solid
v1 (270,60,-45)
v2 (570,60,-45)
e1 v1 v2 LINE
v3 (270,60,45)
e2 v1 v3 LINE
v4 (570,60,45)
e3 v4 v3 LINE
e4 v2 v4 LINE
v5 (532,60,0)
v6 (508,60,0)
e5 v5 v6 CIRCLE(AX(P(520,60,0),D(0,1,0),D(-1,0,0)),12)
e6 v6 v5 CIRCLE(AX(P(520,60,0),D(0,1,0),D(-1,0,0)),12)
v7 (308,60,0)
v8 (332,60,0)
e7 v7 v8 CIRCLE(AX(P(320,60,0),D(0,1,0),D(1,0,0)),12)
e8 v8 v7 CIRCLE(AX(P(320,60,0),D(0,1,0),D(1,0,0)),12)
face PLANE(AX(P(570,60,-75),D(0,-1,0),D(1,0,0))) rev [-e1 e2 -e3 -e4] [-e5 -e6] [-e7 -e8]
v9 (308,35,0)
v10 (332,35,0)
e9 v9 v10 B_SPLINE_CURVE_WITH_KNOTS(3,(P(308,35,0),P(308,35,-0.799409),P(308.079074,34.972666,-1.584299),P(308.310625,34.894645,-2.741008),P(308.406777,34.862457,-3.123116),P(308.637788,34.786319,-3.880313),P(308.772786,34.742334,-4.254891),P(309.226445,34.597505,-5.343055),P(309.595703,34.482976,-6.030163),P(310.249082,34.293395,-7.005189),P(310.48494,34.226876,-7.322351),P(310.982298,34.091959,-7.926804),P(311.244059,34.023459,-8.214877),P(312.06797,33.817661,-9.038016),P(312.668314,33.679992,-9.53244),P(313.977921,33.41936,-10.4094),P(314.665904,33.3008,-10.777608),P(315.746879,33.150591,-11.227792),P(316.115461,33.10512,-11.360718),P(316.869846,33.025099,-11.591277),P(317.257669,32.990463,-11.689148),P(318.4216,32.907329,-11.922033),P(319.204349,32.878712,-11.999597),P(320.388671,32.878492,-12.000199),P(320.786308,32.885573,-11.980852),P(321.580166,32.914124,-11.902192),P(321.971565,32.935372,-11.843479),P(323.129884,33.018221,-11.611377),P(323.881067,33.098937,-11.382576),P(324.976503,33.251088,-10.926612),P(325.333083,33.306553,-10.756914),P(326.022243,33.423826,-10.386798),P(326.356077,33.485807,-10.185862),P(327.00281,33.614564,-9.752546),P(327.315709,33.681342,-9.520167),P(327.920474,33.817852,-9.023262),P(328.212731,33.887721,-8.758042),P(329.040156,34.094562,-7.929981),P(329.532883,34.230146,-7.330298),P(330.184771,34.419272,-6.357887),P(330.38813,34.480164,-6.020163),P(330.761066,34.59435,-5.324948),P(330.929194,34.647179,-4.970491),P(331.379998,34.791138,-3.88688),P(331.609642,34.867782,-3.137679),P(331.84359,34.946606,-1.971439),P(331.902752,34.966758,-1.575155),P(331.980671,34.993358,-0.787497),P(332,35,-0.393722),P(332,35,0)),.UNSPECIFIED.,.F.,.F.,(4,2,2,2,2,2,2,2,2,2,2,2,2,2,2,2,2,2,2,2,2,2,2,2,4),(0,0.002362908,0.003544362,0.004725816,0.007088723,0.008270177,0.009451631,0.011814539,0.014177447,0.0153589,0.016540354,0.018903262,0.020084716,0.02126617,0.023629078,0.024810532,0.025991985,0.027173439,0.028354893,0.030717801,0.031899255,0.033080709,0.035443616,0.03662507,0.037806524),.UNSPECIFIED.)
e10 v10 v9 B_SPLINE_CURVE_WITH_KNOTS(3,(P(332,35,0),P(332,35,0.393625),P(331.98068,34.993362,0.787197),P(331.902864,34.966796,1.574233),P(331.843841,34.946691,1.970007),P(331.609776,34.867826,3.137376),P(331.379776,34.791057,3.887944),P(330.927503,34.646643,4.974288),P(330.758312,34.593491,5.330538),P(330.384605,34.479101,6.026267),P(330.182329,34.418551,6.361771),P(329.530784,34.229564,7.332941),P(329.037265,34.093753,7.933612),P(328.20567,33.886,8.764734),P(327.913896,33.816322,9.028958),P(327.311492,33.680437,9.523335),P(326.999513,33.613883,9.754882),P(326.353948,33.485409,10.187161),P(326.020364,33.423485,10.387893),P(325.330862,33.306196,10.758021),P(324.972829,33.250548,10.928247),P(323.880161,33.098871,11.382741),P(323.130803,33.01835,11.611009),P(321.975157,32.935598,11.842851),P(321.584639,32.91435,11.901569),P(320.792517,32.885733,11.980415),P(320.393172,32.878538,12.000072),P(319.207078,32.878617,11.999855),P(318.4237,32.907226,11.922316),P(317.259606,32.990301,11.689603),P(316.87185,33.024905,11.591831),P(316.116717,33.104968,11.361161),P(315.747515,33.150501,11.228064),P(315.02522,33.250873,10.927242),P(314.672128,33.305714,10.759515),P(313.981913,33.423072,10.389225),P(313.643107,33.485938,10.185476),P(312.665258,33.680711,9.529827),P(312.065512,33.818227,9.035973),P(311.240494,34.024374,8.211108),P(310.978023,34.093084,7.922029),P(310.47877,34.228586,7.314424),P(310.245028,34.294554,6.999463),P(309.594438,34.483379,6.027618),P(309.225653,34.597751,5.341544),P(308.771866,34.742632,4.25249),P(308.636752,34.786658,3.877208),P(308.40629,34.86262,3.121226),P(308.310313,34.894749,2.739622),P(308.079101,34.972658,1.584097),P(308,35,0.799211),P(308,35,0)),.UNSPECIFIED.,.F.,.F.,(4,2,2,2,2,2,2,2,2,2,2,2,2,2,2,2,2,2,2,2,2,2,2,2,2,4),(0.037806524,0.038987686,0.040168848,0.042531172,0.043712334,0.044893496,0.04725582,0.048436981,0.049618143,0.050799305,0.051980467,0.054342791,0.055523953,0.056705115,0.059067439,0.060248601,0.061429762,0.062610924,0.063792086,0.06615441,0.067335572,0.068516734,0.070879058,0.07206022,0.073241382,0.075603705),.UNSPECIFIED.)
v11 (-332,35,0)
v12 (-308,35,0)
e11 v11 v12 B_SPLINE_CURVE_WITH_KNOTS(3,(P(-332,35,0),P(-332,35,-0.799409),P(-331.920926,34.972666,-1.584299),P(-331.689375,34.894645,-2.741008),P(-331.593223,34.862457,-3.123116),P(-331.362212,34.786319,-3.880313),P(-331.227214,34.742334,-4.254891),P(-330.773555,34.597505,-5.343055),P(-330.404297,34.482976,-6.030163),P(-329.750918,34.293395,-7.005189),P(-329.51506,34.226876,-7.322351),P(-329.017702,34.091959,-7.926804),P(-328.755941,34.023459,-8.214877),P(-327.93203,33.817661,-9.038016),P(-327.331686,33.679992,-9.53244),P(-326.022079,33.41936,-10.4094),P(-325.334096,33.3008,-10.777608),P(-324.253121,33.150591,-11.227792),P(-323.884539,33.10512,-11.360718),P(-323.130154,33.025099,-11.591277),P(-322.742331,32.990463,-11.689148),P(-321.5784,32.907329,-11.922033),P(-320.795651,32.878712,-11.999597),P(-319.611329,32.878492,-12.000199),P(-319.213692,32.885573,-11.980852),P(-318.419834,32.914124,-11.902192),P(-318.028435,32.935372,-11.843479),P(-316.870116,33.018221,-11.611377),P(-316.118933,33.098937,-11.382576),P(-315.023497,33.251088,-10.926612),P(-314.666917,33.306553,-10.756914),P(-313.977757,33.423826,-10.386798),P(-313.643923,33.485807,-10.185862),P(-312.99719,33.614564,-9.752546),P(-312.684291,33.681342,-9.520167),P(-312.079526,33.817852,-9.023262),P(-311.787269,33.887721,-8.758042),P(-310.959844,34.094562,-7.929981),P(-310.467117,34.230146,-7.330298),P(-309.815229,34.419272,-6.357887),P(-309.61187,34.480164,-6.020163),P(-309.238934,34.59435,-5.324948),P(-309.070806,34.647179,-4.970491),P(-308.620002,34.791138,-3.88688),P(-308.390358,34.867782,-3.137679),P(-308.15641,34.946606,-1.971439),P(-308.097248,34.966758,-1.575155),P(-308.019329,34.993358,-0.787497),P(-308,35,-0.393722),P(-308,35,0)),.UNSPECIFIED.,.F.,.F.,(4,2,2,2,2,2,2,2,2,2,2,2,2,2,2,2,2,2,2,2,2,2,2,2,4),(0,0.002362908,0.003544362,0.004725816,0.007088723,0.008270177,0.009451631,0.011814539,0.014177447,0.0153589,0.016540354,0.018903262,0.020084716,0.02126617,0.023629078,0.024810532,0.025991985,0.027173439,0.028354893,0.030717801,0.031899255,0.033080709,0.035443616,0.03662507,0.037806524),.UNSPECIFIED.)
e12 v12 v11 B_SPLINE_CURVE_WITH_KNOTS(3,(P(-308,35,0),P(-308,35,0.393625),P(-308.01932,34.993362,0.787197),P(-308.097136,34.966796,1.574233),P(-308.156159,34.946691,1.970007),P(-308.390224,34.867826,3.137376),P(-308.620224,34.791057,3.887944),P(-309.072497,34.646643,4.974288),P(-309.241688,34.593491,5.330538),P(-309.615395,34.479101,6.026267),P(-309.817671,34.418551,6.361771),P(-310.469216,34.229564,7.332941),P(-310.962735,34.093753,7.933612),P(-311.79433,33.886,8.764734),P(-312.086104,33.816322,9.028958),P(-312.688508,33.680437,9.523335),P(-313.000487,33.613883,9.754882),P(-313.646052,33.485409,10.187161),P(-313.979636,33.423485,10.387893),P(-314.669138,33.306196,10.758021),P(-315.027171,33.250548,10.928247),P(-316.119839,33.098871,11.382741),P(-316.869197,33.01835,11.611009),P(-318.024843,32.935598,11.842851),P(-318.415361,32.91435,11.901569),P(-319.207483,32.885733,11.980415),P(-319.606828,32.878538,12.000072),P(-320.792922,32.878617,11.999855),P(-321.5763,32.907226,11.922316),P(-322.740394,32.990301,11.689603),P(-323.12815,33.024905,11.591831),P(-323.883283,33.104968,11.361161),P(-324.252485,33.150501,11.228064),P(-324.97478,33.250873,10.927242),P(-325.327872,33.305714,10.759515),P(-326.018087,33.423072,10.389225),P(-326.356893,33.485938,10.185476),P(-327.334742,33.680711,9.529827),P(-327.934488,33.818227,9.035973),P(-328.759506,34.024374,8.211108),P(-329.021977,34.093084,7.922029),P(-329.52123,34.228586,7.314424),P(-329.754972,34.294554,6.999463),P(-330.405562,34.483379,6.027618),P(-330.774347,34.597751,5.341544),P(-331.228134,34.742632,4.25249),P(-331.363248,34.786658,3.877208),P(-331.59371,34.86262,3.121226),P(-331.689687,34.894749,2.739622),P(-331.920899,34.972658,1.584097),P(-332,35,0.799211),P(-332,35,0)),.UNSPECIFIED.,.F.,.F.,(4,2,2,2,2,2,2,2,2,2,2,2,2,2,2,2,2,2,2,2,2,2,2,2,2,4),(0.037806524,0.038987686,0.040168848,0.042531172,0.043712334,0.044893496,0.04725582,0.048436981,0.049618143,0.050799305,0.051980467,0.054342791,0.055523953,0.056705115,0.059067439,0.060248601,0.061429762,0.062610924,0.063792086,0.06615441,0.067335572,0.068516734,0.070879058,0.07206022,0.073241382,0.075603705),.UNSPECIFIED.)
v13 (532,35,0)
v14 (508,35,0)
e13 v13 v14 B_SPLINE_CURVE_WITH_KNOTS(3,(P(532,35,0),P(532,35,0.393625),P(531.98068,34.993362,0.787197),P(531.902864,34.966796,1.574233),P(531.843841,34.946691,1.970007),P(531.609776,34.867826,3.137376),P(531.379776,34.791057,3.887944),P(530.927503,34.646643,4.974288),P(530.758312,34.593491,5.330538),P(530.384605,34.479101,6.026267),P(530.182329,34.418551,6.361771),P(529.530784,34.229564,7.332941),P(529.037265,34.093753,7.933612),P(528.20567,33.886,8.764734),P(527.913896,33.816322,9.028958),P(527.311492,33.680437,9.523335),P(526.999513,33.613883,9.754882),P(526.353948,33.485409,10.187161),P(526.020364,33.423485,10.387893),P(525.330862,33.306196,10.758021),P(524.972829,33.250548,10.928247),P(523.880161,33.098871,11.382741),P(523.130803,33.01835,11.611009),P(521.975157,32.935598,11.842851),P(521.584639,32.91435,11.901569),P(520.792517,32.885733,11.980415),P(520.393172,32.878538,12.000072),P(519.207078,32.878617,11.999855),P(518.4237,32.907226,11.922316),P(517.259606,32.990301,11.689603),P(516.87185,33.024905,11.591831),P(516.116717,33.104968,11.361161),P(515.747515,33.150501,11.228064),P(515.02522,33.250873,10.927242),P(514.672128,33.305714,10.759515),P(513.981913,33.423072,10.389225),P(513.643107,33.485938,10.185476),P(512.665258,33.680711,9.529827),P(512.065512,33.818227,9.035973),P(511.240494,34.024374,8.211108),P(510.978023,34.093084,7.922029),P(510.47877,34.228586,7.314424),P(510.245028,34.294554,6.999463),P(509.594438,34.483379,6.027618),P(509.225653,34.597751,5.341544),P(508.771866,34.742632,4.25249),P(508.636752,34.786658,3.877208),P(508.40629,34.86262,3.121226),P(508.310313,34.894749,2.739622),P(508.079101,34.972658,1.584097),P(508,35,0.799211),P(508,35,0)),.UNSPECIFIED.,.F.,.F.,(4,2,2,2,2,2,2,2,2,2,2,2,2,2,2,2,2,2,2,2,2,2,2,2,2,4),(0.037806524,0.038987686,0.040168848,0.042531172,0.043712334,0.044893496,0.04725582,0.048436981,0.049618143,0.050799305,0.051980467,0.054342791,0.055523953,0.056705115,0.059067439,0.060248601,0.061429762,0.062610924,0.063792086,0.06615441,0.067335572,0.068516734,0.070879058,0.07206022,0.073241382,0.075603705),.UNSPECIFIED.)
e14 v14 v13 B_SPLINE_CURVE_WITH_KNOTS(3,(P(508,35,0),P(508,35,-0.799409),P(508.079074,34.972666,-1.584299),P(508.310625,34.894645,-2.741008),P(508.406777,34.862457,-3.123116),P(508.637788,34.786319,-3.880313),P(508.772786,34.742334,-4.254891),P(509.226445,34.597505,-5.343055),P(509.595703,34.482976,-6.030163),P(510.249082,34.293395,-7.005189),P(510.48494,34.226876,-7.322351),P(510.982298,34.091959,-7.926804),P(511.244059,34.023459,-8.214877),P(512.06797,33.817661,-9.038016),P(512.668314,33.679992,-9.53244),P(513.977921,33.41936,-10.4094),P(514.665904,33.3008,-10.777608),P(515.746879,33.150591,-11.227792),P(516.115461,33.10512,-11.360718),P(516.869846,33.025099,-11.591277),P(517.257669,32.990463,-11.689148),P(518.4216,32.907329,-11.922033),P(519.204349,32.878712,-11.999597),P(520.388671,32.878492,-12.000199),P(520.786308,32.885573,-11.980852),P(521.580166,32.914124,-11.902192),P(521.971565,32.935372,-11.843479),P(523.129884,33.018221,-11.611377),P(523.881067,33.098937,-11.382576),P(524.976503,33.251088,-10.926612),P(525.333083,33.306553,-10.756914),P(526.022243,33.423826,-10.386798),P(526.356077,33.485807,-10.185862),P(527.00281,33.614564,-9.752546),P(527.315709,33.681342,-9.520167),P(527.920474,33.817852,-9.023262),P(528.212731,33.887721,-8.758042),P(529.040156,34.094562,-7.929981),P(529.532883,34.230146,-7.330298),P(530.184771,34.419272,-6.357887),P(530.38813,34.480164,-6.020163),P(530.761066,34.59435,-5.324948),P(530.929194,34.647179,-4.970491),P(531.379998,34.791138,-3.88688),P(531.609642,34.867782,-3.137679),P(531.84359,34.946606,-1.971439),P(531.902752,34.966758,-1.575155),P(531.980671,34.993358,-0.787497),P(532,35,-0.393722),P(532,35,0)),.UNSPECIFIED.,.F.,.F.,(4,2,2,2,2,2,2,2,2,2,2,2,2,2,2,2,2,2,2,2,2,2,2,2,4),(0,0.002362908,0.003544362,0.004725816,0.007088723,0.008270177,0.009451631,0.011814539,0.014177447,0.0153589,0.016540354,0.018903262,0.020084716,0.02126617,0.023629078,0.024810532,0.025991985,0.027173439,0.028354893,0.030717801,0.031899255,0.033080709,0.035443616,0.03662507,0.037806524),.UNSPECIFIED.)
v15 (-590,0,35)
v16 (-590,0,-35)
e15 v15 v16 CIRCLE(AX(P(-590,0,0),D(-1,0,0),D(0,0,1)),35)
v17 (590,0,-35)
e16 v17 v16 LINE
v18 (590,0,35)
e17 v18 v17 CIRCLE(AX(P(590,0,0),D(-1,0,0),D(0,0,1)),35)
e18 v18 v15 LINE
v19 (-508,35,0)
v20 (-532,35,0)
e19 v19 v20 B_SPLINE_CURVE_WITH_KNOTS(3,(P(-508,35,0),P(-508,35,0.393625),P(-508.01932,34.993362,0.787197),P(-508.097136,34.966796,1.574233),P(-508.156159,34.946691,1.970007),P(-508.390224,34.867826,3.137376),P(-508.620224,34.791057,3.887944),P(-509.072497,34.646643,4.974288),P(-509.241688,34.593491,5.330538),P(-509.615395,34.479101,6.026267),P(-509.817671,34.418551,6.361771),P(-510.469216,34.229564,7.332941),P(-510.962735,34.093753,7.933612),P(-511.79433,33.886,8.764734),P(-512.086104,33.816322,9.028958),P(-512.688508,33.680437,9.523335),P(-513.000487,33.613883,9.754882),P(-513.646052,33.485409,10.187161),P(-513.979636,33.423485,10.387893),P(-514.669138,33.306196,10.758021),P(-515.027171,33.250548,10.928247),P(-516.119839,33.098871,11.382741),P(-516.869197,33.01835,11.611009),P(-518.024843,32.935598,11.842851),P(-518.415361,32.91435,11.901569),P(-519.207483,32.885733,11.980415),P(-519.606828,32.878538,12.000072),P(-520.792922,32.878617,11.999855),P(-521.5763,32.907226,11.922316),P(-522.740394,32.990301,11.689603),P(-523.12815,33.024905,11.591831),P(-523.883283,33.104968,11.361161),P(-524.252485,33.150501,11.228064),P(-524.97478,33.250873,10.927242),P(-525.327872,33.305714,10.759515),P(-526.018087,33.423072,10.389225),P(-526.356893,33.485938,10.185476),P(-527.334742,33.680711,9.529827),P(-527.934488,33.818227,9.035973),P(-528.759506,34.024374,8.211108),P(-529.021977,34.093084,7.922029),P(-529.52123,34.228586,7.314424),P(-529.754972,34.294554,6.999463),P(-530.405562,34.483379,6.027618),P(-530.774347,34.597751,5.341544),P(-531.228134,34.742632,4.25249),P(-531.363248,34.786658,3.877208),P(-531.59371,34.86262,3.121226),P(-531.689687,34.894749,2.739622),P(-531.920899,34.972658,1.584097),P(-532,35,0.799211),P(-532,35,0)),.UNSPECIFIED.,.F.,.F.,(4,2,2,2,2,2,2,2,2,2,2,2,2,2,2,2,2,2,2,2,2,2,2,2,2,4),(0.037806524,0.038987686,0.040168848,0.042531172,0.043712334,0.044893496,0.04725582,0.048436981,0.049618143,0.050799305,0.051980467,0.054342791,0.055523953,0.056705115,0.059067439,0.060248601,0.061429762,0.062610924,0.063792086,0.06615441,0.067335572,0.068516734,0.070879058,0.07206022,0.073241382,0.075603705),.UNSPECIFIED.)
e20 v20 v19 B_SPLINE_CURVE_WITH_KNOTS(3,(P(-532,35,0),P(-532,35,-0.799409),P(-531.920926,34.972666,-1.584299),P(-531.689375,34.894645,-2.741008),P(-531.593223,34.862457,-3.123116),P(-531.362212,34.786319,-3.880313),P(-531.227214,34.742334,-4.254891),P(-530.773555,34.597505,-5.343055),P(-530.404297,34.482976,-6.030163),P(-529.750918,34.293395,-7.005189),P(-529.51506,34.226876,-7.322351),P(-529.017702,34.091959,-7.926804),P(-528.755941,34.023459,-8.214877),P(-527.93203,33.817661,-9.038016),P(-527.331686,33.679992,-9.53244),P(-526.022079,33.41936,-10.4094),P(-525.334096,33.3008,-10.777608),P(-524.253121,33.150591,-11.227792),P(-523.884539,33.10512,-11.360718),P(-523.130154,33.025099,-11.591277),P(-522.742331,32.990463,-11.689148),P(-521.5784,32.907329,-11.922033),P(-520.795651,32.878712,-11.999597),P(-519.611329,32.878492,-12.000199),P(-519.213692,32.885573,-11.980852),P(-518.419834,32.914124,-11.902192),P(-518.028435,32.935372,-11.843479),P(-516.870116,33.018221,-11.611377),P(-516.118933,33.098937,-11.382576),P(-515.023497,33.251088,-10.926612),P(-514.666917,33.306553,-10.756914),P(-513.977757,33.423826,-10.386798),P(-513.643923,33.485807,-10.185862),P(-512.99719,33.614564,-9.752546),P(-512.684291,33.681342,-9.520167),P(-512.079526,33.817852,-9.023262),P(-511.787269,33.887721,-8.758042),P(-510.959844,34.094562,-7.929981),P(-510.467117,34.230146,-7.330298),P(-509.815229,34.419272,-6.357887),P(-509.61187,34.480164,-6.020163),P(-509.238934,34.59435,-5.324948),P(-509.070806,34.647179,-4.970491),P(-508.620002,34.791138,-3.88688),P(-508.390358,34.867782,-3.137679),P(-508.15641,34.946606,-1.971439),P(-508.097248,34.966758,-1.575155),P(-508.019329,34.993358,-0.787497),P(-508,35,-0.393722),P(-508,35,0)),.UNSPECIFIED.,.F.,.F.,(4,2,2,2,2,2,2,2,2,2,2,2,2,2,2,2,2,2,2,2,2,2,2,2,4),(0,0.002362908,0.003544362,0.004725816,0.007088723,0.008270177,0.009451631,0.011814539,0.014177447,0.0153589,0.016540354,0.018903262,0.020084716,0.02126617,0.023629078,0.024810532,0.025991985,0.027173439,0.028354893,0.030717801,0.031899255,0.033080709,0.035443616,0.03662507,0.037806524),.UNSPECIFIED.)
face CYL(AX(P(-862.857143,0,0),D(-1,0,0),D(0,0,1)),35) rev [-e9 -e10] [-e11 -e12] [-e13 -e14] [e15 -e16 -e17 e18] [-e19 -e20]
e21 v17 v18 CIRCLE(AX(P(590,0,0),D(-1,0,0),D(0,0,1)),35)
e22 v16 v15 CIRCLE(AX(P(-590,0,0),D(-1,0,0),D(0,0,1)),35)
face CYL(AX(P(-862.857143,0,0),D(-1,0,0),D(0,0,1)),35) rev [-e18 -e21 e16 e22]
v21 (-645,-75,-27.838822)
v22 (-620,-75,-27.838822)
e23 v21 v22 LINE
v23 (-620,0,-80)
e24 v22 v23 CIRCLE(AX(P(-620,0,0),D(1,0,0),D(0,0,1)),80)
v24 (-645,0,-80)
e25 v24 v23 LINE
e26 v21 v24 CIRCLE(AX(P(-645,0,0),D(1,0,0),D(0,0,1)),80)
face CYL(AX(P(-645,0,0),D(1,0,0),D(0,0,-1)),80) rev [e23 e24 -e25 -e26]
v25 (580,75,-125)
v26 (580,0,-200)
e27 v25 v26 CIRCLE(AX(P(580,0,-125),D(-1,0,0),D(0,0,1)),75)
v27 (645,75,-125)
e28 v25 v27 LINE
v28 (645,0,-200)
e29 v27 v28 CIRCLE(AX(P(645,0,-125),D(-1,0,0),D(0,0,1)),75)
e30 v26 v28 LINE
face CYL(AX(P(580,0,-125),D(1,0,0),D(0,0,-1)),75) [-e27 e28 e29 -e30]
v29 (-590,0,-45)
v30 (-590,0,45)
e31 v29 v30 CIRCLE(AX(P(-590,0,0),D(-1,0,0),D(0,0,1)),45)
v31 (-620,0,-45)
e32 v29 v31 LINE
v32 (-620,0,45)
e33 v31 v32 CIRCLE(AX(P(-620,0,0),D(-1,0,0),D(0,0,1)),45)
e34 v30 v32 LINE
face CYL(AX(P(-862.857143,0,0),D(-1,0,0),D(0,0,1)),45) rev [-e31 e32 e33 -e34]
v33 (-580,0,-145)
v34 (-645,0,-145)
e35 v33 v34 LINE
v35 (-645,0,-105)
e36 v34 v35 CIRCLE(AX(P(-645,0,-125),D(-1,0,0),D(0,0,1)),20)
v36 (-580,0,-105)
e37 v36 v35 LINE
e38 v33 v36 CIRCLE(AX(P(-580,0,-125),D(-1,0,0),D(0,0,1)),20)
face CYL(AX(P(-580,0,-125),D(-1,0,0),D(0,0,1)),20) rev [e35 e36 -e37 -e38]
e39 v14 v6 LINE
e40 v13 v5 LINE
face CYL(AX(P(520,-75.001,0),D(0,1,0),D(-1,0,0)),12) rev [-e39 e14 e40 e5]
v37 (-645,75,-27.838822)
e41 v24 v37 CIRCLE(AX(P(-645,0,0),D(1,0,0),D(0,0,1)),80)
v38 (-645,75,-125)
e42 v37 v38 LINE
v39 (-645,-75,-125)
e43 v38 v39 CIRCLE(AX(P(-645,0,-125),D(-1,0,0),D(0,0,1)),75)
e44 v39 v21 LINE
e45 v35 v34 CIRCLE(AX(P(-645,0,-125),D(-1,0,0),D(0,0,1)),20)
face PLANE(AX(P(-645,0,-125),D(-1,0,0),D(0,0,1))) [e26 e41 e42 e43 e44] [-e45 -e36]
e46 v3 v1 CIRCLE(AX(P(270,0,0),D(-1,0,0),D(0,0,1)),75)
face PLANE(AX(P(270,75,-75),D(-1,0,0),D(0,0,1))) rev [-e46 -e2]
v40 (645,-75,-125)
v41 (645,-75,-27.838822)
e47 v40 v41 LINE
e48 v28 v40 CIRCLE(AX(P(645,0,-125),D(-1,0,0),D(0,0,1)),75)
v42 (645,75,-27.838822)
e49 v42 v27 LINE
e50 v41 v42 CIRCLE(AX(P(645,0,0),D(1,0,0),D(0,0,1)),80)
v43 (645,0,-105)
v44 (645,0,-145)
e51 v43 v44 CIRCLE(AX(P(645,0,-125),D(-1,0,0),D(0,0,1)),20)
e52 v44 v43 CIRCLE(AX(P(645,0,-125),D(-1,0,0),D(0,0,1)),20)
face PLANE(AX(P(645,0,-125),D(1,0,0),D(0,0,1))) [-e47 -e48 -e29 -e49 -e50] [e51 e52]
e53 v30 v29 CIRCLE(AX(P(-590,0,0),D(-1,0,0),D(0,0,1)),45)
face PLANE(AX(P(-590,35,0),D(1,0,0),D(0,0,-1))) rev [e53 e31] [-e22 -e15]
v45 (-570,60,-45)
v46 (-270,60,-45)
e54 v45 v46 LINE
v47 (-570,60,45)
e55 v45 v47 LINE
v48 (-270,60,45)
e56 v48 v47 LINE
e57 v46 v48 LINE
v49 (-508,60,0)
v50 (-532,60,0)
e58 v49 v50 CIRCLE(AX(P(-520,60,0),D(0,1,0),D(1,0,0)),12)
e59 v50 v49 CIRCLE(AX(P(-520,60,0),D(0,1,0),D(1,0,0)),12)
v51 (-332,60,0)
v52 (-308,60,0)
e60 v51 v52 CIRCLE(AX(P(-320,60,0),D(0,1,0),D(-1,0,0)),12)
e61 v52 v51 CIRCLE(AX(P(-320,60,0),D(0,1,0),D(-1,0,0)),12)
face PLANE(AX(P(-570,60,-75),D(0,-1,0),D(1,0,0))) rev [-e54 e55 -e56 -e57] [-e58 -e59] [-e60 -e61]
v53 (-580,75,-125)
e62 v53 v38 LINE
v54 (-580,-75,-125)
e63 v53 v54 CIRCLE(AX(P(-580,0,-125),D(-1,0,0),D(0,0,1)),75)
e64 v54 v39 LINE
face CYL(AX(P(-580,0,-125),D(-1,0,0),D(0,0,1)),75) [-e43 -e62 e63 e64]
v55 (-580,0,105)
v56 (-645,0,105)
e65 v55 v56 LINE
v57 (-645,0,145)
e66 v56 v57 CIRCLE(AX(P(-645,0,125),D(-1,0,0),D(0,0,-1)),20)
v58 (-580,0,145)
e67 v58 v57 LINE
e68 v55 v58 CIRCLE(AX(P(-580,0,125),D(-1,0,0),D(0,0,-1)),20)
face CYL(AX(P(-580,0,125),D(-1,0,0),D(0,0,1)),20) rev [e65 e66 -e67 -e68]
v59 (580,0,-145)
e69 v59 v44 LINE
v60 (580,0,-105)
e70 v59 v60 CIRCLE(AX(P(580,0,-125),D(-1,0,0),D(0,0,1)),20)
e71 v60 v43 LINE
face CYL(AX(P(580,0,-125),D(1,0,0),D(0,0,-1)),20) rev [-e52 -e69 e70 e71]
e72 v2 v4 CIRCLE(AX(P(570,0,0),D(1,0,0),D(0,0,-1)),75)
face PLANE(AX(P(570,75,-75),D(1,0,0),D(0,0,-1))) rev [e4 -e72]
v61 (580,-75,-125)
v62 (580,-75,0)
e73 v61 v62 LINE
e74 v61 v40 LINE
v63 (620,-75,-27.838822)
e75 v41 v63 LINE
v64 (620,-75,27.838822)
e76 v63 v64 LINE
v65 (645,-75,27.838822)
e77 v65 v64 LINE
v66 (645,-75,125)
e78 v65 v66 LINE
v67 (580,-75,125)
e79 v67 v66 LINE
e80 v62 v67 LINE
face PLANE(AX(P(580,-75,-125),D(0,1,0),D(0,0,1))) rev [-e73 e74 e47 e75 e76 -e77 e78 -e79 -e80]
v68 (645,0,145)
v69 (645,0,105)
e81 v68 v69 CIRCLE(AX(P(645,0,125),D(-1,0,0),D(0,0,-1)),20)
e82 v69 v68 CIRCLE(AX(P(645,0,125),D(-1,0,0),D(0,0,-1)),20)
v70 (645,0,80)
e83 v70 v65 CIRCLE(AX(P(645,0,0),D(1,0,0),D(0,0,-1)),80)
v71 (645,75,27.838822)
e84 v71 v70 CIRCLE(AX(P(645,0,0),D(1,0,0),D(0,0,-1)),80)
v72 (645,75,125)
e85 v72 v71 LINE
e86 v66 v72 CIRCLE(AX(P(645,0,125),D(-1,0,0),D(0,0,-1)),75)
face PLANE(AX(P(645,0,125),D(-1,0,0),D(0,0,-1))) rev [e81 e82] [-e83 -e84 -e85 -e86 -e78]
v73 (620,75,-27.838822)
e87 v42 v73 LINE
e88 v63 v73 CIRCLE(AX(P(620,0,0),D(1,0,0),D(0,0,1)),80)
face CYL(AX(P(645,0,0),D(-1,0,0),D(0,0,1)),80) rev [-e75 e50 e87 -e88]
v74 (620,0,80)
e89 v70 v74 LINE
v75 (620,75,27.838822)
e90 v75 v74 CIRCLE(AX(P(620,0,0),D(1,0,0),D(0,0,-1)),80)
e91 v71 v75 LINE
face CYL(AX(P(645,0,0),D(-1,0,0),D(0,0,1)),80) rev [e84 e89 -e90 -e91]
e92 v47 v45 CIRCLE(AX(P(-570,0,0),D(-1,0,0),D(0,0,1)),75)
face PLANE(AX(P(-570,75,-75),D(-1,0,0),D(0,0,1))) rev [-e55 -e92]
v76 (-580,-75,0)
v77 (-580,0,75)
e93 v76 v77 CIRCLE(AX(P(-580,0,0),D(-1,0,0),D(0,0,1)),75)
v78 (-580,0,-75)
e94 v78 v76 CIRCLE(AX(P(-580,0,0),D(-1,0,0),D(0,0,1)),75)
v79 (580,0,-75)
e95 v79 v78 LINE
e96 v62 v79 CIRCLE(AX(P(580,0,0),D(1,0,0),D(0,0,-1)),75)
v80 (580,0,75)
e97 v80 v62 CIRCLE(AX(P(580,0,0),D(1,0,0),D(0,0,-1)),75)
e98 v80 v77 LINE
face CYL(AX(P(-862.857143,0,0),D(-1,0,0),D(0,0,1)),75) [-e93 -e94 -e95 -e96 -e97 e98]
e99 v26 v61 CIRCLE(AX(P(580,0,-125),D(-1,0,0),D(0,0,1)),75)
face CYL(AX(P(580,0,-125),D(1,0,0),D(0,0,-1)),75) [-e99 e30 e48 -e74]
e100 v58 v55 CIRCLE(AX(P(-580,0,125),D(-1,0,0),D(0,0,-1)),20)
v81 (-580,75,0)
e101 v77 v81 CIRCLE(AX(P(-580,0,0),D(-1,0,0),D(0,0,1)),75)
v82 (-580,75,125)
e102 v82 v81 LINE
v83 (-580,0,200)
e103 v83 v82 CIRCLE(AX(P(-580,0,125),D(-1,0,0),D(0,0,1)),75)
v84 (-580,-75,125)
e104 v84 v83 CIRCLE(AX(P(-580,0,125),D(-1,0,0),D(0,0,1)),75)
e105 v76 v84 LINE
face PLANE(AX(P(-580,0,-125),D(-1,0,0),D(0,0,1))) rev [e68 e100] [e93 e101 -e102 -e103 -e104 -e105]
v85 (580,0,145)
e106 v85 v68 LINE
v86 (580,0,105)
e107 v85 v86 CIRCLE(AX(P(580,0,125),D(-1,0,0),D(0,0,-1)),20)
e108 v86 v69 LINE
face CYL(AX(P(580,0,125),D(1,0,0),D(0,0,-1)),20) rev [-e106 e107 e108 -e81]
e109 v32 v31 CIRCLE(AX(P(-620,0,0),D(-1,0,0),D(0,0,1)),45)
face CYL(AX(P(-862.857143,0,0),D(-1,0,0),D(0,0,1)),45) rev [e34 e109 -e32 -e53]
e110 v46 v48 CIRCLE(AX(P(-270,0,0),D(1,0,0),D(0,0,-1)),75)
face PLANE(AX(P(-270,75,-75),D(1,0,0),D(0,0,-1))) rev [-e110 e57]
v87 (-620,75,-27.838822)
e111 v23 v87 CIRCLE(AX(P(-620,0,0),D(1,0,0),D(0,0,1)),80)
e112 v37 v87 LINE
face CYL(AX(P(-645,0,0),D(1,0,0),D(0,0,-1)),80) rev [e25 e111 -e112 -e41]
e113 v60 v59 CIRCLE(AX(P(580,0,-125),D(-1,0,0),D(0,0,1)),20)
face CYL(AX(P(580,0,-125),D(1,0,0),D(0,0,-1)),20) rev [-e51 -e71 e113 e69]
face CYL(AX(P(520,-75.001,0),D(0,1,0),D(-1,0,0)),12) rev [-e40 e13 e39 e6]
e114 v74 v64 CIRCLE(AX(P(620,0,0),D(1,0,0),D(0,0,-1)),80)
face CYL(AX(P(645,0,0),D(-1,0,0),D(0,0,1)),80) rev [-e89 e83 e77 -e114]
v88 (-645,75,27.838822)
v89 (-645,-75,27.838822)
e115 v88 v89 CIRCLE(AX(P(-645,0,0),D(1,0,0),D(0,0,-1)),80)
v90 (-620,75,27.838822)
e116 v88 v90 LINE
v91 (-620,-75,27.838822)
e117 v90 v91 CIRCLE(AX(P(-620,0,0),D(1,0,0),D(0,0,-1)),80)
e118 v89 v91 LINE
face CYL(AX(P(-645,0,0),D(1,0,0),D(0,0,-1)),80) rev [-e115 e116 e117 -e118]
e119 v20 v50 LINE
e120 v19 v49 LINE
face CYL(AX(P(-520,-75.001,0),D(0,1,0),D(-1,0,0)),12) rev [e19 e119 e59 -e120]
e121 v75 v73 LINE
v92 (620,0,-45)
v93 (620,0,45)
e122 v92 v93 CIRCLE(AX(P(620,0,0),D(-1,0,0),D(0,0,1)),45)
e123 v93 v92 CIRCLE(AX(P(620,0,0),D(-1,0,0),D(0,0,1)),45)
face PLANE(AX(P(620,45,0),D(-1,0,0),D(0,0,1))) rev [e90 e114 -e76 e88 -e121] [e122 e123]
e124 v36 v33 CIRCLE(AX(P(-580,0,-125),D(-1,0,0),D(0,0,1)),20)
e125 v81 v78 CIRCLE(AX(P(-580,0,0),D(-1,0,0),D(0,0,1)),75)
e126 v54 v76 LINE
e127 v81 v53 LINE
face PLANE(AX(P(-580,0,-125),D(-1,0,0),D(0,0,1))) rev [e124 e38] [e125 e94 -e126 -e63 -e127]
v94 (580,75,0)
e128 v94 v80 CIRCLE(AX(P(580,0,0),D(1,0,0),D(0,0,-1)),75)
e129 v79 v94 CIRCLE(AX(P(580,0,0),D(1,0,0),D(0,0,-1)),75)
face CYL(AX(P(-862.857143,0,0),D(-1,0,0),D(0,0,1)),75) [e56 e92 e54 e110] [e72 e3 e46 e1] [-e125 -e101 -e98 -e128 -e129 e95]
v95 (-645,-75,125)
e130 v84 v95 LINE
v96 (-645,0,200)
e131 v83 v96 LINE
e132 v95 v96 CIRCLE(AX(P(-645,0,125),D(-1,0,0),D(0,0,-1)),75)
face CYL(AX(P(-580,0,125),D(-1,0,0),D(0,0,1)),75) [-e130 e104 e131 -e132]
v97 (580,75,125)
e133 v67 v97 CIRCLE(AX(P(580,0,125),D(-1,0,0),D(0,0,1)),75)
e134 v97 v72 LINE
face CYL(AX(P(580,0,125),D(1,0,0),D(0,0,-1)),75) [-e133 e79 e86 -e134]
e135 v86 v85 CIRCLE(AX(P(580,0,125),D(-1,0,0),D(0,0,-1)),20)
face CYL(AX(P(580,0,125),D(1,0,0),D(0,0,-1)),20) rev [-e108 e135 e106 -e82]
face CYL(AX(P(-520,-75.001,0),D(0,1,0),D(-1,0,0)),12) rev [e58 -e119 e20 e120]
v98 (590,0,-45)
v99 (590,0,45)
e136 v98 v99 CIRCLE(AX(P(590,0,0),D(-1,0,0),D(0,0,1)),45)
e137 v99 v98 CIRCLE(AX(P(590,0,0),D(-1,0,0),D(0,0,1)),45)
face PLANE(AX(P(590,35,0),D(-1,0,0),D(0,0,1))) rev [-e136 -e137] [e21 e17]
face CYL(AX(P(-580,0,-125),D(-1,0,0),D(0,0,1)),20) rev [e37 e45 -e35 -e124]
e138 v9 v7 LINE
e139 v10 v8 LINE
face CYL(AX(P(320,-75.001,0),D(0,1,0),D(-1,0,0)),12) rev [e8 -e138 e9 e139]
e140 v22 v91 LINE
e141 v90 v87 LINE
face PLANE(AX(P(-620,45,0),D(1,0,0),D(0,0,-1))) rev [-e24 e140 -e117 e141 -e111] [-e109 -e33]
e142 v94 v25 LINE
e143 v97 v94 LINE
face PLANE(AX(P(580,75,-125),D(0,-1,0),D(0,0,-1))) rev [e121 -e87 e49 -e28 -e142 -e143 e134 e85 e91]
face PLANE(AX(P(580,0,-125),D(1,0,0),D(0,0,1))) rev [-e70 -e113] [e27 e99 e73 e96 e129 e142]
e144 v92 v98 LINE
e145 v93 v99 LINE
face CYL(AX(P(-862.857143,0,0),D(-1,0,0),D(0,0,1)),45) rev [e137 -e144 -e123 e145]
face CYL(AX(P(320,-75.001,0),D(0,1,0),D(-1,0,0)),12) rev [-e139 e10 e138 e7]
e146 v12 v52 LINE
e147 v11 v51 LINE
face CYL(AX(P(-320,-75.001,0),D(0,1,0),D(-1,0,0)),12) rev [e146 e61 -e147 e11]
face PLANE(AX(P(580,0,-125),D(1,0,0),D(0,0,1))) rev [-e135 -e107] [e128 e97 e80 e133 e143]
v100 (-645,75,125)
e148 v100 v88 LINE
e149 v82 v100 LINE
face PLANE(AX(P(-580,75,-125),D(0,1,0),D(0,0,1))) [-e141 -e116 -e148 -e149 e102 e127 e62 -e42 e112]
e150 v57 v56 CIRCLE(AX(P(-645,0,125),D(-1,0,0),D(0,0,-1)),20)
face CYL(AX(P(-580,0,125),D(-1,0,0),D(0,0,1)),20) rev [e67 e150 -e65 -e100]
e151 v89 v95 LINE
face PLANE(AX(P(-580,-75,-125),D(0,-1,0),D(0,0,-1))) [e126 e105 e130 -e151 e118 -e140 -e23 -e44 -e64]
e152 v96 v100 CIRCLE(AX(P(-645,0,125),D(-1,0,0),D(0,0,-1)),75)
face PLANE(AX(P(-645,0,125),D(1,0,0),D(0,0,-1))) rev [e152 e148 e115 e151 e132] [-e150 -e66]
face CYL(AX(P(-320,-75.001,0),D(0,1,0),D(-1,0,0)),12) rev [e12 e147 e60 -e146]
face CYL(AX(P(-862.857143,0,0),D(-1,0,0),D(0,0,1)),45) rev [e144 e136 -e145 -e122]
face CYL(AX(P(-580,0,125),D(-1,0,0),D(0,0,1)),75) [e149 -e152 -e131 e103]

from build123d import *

# Parameters (mm, degrees)
CUT_EXTRUDE_1_DEPTH      = 630.007154172
CUT_EXTRUDE_1_DEPTH_BACK = 630.007154172
SKETCH_2_W               = 300
SKETCH_2_H               = 15
CUT_EXTRUDE_2_REACH      = 640.944
CUT_EXTRUDE_2_END_RADIUS = 35
SKETCH_3_R               = 12
SKETCH_4_R               = 20
SKETCH_4_R_2             = 45
BOSS_EXTRUDE_1_DEPTH     = 40
BOSS_EXTRUDE_START       = 25
SKETCH_5_R               = 20
BOSS_EXTRUDE_2_DEPTH     = 25


with BuildPart() as part:
    # Sketch 1 → Revolve 1 (revolve)
    with BuildSketch(Plane.XY, mode=Mode.PRIVATE) as revolve_1_sk:
        Polygon((590, 35), (-590, 35), (-590, 45), (-620, 45), (-620, 75), (620, 75), (620, 45), (590, 45), align=None)
    revolve(revolve_1_sk.sketch.rotate(Axis((-862.857142857, 0, 0), (1, 0, 0)), 90), axis=Axis((-862.857142857, 0, 0), (1, 0, 0)))

    # Sketch 2 → Cut-Extrude 1 (cut, two sides: drawn at the far end of the back side and taken through both)
    with BuildSketch(Plane.XY.offset(-CUT_EXTRUDE_1_DEPTH_BACK)):
        with Locations((-420, 67.5)):
            Rectangle(SKETCH_2_W, SKETCH_2_H)
        with Locations((420, 67.5)):
            Rectangle(SKETCH_2_W, SKETCH_2_H)
    extrude(amount=CUT_EXTRUDE_1_DEPTH + CUT_EXTRUDE_1_DEPTH_BACK, mode=Mode.SUBTRACT)

    # Cut-Extrude 2: up to this cylinder (the profile starts outside it)
    cut_extrude_2_end = Plane(origin=(0, 0, 0), z_dir=(-1, 0, 0)) * Cylinder(CUT_EXTRUDE_2_END_RADIUS, 2392.888, mode=Mode.PRIVATE)
    # Sketch 3 → Cut-Extrude 2 (cut, up to the surface)
    with BuildSketch(Plane(origin=(0, 60, 0), x_dir=(1, 0, 0), z_dir=(0, 1, 0)), mode=Mode.PRIVATE) as cut_extrude_2_sk1:
        with Locations(Location((-320, 0, 0), (0, 0, 180))):
            Circle(SKETCH_3_R)
    cut_extrude_2_tool1 = extrude(cut_extrude_2_sk1.sketch, amount=-CUT_EXTRUDE_2_REACH, mode=Mode.PRIVATE) - cut_extrude_2_end
    add(cut_extrude_2_tool1.solids().sort_by_distance((-320, 60, 0))[0], mode=Mode.SUBTRACT)
    # Sketch 3 → Cut-Extrude 2 (cut, up to the surface)
    with BuildSketch(Plane(origin=(0, 60, 0), x_dir=(1, 0, 0), z_dir=(0, 1, 0)), mode=Mode.PRIVATE) as cut_extrude_2_sk2:
        with Locations(Location((-520, 0, 0), (0, 0, 180))):
            Circle(SKETCH_3_R)
    cut_extrude_2_tool2 = extrude(cut_extrude_2_sk2.sketch, amount=-CUT_EXTRUDE_2_REACH, mode=Mode.PRIVATE) - cut_extrude_2_end
    add(cut_extrude_2_tool2.solids().sort_by_distance((-520, 60, 0))[0], mode=Mode.SUBTRACT)
    # Sketch 3 → Cut-Extrude 2 (cut, up to the surface)
    with BuildSketch(Plane(origin=(0, 60, 0), x_dir=(1, 0, 0), z_dir=(0, 1, 0)), mode=Mode.PRIVATE) as cut_extrude_2_sk3:
        with Locations(Location((520, 0, 0), (0, 0, 180))):
            Circle(SKETCH_3_R)
    cut_extrude_2_tool3 = extrude(cut_extrude_2_sk3.sketch, amount=-CUT_EXTRUDE_2_REACH, mode=Mode.PRIVATE) - cut_extrude_2_end
    add(cut_extrude_2_tool3.solids().sort_by_distance((520, 60, 0))[0], mode=Mode.SUBTRACT)
    # Sketch 3 → Cut-Extrude 2 (cut, up to the surface)
    with BuildSketch(Plane(origin=(0, 60, 0), x_dir=(1, 0, 0), z_dir=(0, 1, 0)), mode=Mode.PRIVATE) as cut_extrude_2_sk4:
        with Locations(Location((320, 0, 0), (0, 0, 180))):
            Circle(SKETCH_3_R)
    cut_extrude_2_tool4 = extrude(cut_extrude_2_sk4.sketch, amount=-CUT_EXTRUDE_2_REACH, mode=Mode.PRIVATE) - cut_extrude_2_end
    add(cut_extrude_2_tool4.solids().sort_by_distance((320, 60, 0))[0], mode=Mode.SUBTRACT)

    # Sketch 4 → Boss-Extrude 1 (add)
    with BuildSketch(Plane.ZY.offset(620)):
        with BuildLine():
            Line((-125, 75), (125, 75))
            ThreePointArc((125, 75), (200, 0), (125, -75))
            Line((125, -75), (-125, -75))
            ThreePointArc((-125, -75), (-200, 0), (-125, 75))
        make_face()
        with Locations((-125, 0)):
            Circle(SKETCH_4_R, mode=Mode.SUBTRACT)
        with Locations(Location((125, 0, 0), (0, 0, 180))):
            Circle(SKETCH_4_R, mode=Mode.SUBTRACT)
        Circle(SKETCH_4_R_2, mode=Mode.SUBTRACT)
    boss_extrude_1 = extrude(amount=-BOSS_EXTRUDE_1_DEPTH)

    # Sketch 5 → Boss-Extrude 2 (add)
    # profile 1 of 2: a face of its own
    with BuildSketch(Plane.ZY.offset(620).offset(BOSS_EXTRUDE_START)):
        with BuildLine():
            Line((-27.838821814, 75), (-125, 75))
            ThreePointArc((-125, 75), (-200, 0), (-125, -75))
            Line((-125, -75), (-27.838821814, -75))
            ThreePointArc((-27.838821814, -75), (-80, 0), (-27.838821814, 75))
        make_face()
        with Locations((-125, 0)):
            Circle(SKETCH_5_R, mode=Mode.SUBTRACT)
    # profile 2 of 2: a face of its own
    with BuildSketch(Plane.ZY.offset(620).offset(BOSS_EXTRUDE_START)):
        with BuildLine():
            Line((125, -75), (27.838821814, -75))
            ThreePointArc((27.838821814, -75), (80, 0), (27.838821814, 75))
            Line((27.838821814, 75), (125, 75))
            ThreePointArc((125, 75), (200, 0), (125, -75))
        make_face()
        with Locations(Location((125, 0, 0), (0, 0, 180))):
            Circle(SKETCH_5_R, mode=Mode.SUBTRACT)
    boss_extrude_2 = extrude(amount=-BOSS_EXTRUDE_2_DEPTH)

    # Mirror 1: Boss-Extrude 1, Boss-Extrude 2 across plane
    add(boss_extrude_1.mirror(Plane(origin=(0, 0, 0), x_dir=(0, 0, 1), z_dir=(1, 0, 0))))
    add(boss_extrude_2.mirror(Plane(origin=(0, 0, 0), x_dir=(0, 0, 1), z_dir=(1, 0, 0))))


solid = part.part
